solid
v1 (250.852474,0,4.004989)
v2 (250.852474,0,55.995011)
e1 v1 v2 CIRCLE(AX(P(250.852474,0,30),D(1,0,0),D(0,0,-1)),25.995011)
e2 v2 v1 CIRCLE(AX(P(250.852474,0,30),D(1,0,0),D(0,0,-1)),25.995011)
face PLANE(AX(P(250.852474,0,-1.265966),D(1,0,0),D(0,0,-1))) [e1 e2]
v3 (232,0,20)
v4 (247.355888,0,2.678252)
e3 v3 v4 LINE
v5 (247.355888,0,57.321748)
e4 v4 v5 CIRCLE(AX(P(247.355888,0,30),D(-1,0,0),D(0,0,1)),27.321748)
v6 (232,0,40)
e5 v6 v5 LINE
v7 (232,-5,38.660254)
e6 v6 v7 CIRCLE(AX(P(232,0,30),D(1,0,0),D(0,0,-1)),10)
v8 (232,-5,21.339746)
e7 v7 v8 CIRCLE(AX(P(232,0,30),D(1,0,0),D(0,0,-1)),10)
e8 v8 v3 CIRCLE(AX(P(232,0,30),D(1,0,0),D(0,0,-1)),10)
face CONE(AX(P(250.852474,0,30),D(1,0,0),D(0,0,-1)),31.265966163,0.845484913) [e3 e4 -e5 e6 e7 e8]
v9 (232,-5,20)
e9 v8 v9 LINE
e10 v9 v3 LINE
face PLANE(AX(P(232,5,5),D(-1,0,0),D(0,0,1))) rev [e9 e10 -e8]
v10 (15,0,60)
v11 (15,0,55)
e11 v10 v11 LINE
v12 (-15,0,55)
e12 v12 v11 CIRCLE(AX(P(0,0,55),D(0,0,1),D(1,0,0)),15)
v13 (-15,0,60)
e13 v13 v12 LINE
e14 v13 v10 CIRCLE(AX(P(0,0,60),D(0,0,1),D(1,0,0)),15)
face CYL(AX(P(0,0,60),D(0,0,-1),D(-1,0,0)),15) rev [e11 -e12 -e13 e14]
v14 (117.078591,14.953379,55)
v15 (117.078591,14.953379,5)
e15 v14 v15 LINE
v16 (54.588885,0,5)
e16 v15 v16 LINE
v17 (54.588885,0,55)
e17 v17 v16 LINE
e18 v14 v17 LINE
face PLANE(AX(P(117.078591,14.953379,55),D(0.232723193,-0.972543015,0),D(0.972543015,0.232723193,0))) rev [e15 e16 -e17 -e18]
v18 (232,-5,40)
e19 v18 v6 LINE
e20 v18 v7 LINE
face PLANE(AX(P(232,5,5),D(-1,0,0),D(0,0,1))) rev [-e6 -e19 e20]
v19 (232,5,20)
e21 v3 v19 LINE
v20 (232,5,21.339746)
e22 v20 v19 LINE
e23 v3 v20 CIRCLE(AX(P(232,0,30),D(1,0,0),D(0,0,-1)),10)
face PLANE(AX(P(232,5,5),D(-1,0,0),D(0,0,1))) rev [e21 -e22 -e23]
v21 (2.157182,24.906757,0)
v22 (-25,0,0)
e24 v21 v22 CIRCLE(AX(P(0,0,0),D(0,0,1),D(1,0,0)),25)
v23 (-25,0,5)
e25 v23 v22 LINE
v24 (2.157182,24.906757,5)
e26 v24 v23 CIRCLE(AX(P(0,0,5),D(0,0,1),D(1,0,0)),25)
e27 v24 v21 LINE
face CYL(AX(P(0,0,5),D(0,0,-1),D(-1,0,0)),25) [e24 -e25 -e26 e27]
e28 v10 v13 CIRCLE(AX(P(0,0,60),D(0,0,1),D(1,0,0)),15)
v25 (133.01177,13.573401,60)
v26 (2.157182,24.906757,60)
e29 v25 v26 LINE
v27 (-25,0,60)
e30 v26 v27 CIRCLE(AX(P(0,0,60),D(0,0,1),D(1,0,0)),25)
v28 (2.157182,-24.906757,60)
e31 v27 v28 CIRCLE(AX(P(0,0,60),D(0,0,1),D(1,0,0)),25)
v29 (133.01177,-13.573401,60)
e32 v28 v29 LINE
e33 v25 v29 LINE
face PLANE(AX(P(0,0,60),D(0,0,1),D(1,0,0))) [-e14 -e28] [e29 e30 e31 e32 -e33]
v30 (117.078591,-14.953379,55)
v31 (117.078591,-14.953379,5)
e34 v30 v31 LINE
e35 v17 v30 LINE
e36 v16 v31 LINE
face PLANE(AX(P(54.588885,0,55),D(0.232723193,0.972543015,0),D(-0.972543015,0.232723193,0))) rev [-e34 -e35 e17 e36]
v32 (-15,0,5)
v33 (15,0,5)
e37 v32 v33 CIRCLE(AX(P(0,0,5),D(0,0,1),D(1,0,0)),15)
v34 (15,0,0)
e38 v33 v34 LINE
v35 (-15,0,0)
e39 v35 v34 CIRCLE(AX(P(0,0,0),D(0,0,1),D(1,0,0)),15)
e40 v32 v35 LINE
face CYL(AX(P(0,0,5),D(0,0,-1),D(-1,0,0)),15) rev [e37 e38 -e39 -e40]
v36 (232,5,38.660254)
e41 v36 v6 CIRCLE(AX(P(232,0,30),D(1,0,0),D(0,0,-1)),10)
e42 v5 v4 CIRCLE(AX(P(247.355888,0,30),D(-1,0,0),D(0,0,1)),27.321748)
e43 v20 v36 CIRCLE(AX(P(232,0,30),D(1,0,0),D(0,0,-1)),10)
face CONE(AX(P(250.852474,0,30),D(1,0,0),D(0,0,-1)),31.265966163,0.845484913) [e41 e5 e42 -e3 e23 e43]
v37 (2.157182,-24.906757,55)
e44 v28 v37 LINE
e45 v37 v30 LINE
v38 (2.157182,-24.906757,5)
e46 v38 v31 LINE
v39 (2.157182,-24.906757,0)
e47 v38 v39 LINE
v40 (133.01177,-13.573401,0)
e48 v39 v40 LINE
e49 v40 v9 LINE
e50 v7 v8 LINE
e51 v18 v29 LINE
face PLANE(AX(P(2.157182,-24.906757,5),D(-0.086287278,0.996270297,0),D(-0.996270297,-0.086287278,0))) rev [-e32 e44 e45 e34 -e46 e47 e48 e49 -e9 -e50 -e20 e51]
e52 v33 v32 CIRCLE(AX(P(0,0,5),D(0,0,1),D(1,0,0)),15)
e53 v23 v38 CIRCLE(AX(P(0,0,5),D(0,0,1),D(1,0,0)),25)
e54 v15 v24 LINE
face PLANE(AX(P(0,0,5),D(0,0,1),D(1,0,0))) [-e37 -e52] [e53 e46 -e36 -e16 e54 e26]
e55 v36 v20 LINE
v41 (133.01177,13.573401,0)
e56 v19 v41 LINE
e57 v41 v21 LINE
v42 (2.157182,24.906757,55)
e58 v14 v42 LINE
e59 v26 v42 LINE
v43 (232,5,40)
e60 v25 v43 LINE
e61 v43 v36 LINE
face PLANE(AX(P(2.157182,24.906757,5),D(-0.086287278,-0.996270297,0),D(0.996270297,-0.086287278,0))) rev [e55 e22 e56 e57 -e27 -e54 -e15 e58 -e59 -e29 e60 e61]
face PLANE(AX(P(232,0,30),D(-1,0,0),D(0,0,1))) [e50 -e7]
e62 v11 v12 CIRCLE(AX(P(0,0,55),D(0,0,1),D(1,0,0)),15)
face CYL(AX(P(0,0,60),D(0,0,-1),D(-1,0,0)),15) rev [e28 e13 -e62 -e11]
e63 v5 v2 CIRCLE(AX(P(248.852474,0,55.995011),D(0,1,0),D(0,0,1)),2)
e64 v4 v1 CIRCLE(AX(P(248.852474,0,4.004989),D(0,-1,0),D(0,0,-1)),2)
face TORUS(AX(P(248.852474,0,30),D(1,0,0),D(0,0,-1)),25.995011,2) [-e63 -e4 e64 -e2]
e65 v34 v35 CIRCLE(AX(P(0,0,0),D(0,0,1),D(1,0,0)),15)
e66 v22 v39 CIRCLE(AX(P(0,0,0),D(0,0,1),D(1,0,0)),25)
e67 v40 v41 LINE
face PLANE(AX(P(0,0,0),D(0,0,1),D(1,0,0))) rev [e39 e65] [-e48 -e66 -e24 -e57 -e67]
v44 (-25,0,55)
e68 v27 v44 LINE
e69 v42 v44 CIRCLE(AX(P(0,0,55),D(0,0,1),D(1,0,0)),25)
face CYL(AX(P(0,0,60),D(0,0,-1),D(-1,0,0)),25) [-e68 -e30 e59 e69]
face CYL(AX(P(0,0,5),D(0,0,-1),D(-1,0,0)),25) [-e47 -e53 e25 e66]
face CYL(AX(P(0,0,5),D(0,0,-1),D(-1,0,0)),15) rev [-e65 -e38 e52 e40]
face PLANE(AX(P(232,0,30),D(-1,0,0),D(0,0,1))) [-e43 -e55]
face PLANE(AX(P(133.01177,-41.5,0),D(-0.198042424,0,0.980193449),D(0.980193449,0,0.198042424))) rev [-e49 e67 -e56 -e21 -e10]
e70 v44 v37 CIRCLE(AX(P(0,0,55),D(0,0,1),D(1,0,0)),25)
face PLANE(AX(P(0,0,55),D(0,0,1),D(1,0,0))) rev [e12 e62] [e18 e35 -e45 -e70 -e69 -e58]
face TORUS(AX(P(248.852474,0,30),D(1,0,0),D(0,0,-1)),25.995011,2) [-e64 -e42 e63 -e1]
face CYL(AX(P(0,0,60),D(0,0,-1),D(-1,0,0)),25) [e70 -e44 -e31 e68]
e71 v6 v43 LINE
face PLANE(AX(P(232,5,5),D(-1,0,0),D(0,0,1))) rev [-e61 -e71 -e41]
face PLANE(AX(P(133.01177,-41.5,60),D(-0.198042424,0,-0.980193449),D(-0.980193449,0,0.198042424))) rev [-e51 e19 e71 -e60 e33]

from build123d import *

# Parameters (mm, degrees)
SKETCH13_R          = 15
BOSS_EXTRUDE6_DEPTH = 5
BOSS_EXTRUDE7_DEPTH = 50
BOSS_EXTRUDE8_START = 50
SKETCH15_R          = 15
BOSS_EXTRUDE8_DEPTH = 5
CUT_EXTRUDE2_DEPTH  = 41.5
FILLET2_R           = 2


with BuildPart() as part:
    # Sketch13 → Boss-Extrude6 (new body)
    with BuildSketch(Plane.XY):
        with BuildLine():
            Line((2.157181952, 24.906757437), (232, 5))
            Line((232, 5), (232, -5))
            Line((232, -5), (2.157181952, -24.906757437))
            ThreePointArc((2.157181952, -24.906757437), (-25, 0), (2.157181952, 24.906757437))
        make_face()
        Circle(SKETCH13_R, mode=Mode.SUBTRACT)
    extrude(amount=BOSS_EXTRUDE6_DEPTH)

    # Sketch14 → Boss-Extrude7 (add)
    with BuildSketch(Plane.XY.offset(5)):
        Polygon((232, 5), (117.078590976, 14.953378719), (54.588884616, 0), (117.078590976, -14.953378719), (232, -5), align=None)
    extrude(amount=BOSS_EXTRUDE7_DEPTH)

    # Sketch15 → Boss-Extrude8 (add)
    with BuildSketch(Plane.XY.offset(5).offset(BOSS_EXTRUDE8_START)):
        with BuildLine():
            Line((117.078590976, 14.953378719), (2.157181952, 24.906757437))
            ThreePointArc((2.157181952, 24.906757437), (-25, 0), (2.157181952, -24.906757437))
            Line((2.157181952, -24.906757437), (117.078590976, -14.953378719))
            Line((117.078590976, -14.953378719), (232, -5))
            Line((232, -5), (232, 5))
            Line((232, 5), (117.078590976, 14.953378719))
        make_face()
        Circle(SKETCH15_R, mode=Mode.SUBTRACT)
    extrude(amount=BOSS_EXTRUDE8_DEPTH)

    # Sketch16 → Cut-Extrude2 (cut, symmetric)
    with BuildSketch(Plane(origin=(0, 0, 0), x_dir=(1, 0, 0), z_dir=(0, 1, 0))):
        Polygon((232, 0), (133.011770042, 0), (232, -20), align=None)
        Polygon((232, -40), (232, -60), (133.011770042, -60), align=None)
    extrude(amount=CUT_EXTRUDE2_DEPTH, both=True, mode=Mode.SUBTRACT)

    # Sketch20 → Revolve4 (revolve)
    with BuildSketch(Plane(origin=(0, 0, 0), x_dir=(1, 0, 0), z_dir=(0, 1, 0))):
        Polygon((232, -30), (232, -20), (250.852474196, 1.265966163), (250.852474196, -30), align=None)
    revolve(axis=Axis((250.852474196, 0, 30), (-1, 0, 0)))

    # Fillet2
    fillet2_edges = [part.edges().sort_by_distance(p)[0] for p in [
        (250.852474196, 0, 61.265966163),
    ]]
    fillet(fillet2_edges, radius=FILLET2_R)


solid = part.part
